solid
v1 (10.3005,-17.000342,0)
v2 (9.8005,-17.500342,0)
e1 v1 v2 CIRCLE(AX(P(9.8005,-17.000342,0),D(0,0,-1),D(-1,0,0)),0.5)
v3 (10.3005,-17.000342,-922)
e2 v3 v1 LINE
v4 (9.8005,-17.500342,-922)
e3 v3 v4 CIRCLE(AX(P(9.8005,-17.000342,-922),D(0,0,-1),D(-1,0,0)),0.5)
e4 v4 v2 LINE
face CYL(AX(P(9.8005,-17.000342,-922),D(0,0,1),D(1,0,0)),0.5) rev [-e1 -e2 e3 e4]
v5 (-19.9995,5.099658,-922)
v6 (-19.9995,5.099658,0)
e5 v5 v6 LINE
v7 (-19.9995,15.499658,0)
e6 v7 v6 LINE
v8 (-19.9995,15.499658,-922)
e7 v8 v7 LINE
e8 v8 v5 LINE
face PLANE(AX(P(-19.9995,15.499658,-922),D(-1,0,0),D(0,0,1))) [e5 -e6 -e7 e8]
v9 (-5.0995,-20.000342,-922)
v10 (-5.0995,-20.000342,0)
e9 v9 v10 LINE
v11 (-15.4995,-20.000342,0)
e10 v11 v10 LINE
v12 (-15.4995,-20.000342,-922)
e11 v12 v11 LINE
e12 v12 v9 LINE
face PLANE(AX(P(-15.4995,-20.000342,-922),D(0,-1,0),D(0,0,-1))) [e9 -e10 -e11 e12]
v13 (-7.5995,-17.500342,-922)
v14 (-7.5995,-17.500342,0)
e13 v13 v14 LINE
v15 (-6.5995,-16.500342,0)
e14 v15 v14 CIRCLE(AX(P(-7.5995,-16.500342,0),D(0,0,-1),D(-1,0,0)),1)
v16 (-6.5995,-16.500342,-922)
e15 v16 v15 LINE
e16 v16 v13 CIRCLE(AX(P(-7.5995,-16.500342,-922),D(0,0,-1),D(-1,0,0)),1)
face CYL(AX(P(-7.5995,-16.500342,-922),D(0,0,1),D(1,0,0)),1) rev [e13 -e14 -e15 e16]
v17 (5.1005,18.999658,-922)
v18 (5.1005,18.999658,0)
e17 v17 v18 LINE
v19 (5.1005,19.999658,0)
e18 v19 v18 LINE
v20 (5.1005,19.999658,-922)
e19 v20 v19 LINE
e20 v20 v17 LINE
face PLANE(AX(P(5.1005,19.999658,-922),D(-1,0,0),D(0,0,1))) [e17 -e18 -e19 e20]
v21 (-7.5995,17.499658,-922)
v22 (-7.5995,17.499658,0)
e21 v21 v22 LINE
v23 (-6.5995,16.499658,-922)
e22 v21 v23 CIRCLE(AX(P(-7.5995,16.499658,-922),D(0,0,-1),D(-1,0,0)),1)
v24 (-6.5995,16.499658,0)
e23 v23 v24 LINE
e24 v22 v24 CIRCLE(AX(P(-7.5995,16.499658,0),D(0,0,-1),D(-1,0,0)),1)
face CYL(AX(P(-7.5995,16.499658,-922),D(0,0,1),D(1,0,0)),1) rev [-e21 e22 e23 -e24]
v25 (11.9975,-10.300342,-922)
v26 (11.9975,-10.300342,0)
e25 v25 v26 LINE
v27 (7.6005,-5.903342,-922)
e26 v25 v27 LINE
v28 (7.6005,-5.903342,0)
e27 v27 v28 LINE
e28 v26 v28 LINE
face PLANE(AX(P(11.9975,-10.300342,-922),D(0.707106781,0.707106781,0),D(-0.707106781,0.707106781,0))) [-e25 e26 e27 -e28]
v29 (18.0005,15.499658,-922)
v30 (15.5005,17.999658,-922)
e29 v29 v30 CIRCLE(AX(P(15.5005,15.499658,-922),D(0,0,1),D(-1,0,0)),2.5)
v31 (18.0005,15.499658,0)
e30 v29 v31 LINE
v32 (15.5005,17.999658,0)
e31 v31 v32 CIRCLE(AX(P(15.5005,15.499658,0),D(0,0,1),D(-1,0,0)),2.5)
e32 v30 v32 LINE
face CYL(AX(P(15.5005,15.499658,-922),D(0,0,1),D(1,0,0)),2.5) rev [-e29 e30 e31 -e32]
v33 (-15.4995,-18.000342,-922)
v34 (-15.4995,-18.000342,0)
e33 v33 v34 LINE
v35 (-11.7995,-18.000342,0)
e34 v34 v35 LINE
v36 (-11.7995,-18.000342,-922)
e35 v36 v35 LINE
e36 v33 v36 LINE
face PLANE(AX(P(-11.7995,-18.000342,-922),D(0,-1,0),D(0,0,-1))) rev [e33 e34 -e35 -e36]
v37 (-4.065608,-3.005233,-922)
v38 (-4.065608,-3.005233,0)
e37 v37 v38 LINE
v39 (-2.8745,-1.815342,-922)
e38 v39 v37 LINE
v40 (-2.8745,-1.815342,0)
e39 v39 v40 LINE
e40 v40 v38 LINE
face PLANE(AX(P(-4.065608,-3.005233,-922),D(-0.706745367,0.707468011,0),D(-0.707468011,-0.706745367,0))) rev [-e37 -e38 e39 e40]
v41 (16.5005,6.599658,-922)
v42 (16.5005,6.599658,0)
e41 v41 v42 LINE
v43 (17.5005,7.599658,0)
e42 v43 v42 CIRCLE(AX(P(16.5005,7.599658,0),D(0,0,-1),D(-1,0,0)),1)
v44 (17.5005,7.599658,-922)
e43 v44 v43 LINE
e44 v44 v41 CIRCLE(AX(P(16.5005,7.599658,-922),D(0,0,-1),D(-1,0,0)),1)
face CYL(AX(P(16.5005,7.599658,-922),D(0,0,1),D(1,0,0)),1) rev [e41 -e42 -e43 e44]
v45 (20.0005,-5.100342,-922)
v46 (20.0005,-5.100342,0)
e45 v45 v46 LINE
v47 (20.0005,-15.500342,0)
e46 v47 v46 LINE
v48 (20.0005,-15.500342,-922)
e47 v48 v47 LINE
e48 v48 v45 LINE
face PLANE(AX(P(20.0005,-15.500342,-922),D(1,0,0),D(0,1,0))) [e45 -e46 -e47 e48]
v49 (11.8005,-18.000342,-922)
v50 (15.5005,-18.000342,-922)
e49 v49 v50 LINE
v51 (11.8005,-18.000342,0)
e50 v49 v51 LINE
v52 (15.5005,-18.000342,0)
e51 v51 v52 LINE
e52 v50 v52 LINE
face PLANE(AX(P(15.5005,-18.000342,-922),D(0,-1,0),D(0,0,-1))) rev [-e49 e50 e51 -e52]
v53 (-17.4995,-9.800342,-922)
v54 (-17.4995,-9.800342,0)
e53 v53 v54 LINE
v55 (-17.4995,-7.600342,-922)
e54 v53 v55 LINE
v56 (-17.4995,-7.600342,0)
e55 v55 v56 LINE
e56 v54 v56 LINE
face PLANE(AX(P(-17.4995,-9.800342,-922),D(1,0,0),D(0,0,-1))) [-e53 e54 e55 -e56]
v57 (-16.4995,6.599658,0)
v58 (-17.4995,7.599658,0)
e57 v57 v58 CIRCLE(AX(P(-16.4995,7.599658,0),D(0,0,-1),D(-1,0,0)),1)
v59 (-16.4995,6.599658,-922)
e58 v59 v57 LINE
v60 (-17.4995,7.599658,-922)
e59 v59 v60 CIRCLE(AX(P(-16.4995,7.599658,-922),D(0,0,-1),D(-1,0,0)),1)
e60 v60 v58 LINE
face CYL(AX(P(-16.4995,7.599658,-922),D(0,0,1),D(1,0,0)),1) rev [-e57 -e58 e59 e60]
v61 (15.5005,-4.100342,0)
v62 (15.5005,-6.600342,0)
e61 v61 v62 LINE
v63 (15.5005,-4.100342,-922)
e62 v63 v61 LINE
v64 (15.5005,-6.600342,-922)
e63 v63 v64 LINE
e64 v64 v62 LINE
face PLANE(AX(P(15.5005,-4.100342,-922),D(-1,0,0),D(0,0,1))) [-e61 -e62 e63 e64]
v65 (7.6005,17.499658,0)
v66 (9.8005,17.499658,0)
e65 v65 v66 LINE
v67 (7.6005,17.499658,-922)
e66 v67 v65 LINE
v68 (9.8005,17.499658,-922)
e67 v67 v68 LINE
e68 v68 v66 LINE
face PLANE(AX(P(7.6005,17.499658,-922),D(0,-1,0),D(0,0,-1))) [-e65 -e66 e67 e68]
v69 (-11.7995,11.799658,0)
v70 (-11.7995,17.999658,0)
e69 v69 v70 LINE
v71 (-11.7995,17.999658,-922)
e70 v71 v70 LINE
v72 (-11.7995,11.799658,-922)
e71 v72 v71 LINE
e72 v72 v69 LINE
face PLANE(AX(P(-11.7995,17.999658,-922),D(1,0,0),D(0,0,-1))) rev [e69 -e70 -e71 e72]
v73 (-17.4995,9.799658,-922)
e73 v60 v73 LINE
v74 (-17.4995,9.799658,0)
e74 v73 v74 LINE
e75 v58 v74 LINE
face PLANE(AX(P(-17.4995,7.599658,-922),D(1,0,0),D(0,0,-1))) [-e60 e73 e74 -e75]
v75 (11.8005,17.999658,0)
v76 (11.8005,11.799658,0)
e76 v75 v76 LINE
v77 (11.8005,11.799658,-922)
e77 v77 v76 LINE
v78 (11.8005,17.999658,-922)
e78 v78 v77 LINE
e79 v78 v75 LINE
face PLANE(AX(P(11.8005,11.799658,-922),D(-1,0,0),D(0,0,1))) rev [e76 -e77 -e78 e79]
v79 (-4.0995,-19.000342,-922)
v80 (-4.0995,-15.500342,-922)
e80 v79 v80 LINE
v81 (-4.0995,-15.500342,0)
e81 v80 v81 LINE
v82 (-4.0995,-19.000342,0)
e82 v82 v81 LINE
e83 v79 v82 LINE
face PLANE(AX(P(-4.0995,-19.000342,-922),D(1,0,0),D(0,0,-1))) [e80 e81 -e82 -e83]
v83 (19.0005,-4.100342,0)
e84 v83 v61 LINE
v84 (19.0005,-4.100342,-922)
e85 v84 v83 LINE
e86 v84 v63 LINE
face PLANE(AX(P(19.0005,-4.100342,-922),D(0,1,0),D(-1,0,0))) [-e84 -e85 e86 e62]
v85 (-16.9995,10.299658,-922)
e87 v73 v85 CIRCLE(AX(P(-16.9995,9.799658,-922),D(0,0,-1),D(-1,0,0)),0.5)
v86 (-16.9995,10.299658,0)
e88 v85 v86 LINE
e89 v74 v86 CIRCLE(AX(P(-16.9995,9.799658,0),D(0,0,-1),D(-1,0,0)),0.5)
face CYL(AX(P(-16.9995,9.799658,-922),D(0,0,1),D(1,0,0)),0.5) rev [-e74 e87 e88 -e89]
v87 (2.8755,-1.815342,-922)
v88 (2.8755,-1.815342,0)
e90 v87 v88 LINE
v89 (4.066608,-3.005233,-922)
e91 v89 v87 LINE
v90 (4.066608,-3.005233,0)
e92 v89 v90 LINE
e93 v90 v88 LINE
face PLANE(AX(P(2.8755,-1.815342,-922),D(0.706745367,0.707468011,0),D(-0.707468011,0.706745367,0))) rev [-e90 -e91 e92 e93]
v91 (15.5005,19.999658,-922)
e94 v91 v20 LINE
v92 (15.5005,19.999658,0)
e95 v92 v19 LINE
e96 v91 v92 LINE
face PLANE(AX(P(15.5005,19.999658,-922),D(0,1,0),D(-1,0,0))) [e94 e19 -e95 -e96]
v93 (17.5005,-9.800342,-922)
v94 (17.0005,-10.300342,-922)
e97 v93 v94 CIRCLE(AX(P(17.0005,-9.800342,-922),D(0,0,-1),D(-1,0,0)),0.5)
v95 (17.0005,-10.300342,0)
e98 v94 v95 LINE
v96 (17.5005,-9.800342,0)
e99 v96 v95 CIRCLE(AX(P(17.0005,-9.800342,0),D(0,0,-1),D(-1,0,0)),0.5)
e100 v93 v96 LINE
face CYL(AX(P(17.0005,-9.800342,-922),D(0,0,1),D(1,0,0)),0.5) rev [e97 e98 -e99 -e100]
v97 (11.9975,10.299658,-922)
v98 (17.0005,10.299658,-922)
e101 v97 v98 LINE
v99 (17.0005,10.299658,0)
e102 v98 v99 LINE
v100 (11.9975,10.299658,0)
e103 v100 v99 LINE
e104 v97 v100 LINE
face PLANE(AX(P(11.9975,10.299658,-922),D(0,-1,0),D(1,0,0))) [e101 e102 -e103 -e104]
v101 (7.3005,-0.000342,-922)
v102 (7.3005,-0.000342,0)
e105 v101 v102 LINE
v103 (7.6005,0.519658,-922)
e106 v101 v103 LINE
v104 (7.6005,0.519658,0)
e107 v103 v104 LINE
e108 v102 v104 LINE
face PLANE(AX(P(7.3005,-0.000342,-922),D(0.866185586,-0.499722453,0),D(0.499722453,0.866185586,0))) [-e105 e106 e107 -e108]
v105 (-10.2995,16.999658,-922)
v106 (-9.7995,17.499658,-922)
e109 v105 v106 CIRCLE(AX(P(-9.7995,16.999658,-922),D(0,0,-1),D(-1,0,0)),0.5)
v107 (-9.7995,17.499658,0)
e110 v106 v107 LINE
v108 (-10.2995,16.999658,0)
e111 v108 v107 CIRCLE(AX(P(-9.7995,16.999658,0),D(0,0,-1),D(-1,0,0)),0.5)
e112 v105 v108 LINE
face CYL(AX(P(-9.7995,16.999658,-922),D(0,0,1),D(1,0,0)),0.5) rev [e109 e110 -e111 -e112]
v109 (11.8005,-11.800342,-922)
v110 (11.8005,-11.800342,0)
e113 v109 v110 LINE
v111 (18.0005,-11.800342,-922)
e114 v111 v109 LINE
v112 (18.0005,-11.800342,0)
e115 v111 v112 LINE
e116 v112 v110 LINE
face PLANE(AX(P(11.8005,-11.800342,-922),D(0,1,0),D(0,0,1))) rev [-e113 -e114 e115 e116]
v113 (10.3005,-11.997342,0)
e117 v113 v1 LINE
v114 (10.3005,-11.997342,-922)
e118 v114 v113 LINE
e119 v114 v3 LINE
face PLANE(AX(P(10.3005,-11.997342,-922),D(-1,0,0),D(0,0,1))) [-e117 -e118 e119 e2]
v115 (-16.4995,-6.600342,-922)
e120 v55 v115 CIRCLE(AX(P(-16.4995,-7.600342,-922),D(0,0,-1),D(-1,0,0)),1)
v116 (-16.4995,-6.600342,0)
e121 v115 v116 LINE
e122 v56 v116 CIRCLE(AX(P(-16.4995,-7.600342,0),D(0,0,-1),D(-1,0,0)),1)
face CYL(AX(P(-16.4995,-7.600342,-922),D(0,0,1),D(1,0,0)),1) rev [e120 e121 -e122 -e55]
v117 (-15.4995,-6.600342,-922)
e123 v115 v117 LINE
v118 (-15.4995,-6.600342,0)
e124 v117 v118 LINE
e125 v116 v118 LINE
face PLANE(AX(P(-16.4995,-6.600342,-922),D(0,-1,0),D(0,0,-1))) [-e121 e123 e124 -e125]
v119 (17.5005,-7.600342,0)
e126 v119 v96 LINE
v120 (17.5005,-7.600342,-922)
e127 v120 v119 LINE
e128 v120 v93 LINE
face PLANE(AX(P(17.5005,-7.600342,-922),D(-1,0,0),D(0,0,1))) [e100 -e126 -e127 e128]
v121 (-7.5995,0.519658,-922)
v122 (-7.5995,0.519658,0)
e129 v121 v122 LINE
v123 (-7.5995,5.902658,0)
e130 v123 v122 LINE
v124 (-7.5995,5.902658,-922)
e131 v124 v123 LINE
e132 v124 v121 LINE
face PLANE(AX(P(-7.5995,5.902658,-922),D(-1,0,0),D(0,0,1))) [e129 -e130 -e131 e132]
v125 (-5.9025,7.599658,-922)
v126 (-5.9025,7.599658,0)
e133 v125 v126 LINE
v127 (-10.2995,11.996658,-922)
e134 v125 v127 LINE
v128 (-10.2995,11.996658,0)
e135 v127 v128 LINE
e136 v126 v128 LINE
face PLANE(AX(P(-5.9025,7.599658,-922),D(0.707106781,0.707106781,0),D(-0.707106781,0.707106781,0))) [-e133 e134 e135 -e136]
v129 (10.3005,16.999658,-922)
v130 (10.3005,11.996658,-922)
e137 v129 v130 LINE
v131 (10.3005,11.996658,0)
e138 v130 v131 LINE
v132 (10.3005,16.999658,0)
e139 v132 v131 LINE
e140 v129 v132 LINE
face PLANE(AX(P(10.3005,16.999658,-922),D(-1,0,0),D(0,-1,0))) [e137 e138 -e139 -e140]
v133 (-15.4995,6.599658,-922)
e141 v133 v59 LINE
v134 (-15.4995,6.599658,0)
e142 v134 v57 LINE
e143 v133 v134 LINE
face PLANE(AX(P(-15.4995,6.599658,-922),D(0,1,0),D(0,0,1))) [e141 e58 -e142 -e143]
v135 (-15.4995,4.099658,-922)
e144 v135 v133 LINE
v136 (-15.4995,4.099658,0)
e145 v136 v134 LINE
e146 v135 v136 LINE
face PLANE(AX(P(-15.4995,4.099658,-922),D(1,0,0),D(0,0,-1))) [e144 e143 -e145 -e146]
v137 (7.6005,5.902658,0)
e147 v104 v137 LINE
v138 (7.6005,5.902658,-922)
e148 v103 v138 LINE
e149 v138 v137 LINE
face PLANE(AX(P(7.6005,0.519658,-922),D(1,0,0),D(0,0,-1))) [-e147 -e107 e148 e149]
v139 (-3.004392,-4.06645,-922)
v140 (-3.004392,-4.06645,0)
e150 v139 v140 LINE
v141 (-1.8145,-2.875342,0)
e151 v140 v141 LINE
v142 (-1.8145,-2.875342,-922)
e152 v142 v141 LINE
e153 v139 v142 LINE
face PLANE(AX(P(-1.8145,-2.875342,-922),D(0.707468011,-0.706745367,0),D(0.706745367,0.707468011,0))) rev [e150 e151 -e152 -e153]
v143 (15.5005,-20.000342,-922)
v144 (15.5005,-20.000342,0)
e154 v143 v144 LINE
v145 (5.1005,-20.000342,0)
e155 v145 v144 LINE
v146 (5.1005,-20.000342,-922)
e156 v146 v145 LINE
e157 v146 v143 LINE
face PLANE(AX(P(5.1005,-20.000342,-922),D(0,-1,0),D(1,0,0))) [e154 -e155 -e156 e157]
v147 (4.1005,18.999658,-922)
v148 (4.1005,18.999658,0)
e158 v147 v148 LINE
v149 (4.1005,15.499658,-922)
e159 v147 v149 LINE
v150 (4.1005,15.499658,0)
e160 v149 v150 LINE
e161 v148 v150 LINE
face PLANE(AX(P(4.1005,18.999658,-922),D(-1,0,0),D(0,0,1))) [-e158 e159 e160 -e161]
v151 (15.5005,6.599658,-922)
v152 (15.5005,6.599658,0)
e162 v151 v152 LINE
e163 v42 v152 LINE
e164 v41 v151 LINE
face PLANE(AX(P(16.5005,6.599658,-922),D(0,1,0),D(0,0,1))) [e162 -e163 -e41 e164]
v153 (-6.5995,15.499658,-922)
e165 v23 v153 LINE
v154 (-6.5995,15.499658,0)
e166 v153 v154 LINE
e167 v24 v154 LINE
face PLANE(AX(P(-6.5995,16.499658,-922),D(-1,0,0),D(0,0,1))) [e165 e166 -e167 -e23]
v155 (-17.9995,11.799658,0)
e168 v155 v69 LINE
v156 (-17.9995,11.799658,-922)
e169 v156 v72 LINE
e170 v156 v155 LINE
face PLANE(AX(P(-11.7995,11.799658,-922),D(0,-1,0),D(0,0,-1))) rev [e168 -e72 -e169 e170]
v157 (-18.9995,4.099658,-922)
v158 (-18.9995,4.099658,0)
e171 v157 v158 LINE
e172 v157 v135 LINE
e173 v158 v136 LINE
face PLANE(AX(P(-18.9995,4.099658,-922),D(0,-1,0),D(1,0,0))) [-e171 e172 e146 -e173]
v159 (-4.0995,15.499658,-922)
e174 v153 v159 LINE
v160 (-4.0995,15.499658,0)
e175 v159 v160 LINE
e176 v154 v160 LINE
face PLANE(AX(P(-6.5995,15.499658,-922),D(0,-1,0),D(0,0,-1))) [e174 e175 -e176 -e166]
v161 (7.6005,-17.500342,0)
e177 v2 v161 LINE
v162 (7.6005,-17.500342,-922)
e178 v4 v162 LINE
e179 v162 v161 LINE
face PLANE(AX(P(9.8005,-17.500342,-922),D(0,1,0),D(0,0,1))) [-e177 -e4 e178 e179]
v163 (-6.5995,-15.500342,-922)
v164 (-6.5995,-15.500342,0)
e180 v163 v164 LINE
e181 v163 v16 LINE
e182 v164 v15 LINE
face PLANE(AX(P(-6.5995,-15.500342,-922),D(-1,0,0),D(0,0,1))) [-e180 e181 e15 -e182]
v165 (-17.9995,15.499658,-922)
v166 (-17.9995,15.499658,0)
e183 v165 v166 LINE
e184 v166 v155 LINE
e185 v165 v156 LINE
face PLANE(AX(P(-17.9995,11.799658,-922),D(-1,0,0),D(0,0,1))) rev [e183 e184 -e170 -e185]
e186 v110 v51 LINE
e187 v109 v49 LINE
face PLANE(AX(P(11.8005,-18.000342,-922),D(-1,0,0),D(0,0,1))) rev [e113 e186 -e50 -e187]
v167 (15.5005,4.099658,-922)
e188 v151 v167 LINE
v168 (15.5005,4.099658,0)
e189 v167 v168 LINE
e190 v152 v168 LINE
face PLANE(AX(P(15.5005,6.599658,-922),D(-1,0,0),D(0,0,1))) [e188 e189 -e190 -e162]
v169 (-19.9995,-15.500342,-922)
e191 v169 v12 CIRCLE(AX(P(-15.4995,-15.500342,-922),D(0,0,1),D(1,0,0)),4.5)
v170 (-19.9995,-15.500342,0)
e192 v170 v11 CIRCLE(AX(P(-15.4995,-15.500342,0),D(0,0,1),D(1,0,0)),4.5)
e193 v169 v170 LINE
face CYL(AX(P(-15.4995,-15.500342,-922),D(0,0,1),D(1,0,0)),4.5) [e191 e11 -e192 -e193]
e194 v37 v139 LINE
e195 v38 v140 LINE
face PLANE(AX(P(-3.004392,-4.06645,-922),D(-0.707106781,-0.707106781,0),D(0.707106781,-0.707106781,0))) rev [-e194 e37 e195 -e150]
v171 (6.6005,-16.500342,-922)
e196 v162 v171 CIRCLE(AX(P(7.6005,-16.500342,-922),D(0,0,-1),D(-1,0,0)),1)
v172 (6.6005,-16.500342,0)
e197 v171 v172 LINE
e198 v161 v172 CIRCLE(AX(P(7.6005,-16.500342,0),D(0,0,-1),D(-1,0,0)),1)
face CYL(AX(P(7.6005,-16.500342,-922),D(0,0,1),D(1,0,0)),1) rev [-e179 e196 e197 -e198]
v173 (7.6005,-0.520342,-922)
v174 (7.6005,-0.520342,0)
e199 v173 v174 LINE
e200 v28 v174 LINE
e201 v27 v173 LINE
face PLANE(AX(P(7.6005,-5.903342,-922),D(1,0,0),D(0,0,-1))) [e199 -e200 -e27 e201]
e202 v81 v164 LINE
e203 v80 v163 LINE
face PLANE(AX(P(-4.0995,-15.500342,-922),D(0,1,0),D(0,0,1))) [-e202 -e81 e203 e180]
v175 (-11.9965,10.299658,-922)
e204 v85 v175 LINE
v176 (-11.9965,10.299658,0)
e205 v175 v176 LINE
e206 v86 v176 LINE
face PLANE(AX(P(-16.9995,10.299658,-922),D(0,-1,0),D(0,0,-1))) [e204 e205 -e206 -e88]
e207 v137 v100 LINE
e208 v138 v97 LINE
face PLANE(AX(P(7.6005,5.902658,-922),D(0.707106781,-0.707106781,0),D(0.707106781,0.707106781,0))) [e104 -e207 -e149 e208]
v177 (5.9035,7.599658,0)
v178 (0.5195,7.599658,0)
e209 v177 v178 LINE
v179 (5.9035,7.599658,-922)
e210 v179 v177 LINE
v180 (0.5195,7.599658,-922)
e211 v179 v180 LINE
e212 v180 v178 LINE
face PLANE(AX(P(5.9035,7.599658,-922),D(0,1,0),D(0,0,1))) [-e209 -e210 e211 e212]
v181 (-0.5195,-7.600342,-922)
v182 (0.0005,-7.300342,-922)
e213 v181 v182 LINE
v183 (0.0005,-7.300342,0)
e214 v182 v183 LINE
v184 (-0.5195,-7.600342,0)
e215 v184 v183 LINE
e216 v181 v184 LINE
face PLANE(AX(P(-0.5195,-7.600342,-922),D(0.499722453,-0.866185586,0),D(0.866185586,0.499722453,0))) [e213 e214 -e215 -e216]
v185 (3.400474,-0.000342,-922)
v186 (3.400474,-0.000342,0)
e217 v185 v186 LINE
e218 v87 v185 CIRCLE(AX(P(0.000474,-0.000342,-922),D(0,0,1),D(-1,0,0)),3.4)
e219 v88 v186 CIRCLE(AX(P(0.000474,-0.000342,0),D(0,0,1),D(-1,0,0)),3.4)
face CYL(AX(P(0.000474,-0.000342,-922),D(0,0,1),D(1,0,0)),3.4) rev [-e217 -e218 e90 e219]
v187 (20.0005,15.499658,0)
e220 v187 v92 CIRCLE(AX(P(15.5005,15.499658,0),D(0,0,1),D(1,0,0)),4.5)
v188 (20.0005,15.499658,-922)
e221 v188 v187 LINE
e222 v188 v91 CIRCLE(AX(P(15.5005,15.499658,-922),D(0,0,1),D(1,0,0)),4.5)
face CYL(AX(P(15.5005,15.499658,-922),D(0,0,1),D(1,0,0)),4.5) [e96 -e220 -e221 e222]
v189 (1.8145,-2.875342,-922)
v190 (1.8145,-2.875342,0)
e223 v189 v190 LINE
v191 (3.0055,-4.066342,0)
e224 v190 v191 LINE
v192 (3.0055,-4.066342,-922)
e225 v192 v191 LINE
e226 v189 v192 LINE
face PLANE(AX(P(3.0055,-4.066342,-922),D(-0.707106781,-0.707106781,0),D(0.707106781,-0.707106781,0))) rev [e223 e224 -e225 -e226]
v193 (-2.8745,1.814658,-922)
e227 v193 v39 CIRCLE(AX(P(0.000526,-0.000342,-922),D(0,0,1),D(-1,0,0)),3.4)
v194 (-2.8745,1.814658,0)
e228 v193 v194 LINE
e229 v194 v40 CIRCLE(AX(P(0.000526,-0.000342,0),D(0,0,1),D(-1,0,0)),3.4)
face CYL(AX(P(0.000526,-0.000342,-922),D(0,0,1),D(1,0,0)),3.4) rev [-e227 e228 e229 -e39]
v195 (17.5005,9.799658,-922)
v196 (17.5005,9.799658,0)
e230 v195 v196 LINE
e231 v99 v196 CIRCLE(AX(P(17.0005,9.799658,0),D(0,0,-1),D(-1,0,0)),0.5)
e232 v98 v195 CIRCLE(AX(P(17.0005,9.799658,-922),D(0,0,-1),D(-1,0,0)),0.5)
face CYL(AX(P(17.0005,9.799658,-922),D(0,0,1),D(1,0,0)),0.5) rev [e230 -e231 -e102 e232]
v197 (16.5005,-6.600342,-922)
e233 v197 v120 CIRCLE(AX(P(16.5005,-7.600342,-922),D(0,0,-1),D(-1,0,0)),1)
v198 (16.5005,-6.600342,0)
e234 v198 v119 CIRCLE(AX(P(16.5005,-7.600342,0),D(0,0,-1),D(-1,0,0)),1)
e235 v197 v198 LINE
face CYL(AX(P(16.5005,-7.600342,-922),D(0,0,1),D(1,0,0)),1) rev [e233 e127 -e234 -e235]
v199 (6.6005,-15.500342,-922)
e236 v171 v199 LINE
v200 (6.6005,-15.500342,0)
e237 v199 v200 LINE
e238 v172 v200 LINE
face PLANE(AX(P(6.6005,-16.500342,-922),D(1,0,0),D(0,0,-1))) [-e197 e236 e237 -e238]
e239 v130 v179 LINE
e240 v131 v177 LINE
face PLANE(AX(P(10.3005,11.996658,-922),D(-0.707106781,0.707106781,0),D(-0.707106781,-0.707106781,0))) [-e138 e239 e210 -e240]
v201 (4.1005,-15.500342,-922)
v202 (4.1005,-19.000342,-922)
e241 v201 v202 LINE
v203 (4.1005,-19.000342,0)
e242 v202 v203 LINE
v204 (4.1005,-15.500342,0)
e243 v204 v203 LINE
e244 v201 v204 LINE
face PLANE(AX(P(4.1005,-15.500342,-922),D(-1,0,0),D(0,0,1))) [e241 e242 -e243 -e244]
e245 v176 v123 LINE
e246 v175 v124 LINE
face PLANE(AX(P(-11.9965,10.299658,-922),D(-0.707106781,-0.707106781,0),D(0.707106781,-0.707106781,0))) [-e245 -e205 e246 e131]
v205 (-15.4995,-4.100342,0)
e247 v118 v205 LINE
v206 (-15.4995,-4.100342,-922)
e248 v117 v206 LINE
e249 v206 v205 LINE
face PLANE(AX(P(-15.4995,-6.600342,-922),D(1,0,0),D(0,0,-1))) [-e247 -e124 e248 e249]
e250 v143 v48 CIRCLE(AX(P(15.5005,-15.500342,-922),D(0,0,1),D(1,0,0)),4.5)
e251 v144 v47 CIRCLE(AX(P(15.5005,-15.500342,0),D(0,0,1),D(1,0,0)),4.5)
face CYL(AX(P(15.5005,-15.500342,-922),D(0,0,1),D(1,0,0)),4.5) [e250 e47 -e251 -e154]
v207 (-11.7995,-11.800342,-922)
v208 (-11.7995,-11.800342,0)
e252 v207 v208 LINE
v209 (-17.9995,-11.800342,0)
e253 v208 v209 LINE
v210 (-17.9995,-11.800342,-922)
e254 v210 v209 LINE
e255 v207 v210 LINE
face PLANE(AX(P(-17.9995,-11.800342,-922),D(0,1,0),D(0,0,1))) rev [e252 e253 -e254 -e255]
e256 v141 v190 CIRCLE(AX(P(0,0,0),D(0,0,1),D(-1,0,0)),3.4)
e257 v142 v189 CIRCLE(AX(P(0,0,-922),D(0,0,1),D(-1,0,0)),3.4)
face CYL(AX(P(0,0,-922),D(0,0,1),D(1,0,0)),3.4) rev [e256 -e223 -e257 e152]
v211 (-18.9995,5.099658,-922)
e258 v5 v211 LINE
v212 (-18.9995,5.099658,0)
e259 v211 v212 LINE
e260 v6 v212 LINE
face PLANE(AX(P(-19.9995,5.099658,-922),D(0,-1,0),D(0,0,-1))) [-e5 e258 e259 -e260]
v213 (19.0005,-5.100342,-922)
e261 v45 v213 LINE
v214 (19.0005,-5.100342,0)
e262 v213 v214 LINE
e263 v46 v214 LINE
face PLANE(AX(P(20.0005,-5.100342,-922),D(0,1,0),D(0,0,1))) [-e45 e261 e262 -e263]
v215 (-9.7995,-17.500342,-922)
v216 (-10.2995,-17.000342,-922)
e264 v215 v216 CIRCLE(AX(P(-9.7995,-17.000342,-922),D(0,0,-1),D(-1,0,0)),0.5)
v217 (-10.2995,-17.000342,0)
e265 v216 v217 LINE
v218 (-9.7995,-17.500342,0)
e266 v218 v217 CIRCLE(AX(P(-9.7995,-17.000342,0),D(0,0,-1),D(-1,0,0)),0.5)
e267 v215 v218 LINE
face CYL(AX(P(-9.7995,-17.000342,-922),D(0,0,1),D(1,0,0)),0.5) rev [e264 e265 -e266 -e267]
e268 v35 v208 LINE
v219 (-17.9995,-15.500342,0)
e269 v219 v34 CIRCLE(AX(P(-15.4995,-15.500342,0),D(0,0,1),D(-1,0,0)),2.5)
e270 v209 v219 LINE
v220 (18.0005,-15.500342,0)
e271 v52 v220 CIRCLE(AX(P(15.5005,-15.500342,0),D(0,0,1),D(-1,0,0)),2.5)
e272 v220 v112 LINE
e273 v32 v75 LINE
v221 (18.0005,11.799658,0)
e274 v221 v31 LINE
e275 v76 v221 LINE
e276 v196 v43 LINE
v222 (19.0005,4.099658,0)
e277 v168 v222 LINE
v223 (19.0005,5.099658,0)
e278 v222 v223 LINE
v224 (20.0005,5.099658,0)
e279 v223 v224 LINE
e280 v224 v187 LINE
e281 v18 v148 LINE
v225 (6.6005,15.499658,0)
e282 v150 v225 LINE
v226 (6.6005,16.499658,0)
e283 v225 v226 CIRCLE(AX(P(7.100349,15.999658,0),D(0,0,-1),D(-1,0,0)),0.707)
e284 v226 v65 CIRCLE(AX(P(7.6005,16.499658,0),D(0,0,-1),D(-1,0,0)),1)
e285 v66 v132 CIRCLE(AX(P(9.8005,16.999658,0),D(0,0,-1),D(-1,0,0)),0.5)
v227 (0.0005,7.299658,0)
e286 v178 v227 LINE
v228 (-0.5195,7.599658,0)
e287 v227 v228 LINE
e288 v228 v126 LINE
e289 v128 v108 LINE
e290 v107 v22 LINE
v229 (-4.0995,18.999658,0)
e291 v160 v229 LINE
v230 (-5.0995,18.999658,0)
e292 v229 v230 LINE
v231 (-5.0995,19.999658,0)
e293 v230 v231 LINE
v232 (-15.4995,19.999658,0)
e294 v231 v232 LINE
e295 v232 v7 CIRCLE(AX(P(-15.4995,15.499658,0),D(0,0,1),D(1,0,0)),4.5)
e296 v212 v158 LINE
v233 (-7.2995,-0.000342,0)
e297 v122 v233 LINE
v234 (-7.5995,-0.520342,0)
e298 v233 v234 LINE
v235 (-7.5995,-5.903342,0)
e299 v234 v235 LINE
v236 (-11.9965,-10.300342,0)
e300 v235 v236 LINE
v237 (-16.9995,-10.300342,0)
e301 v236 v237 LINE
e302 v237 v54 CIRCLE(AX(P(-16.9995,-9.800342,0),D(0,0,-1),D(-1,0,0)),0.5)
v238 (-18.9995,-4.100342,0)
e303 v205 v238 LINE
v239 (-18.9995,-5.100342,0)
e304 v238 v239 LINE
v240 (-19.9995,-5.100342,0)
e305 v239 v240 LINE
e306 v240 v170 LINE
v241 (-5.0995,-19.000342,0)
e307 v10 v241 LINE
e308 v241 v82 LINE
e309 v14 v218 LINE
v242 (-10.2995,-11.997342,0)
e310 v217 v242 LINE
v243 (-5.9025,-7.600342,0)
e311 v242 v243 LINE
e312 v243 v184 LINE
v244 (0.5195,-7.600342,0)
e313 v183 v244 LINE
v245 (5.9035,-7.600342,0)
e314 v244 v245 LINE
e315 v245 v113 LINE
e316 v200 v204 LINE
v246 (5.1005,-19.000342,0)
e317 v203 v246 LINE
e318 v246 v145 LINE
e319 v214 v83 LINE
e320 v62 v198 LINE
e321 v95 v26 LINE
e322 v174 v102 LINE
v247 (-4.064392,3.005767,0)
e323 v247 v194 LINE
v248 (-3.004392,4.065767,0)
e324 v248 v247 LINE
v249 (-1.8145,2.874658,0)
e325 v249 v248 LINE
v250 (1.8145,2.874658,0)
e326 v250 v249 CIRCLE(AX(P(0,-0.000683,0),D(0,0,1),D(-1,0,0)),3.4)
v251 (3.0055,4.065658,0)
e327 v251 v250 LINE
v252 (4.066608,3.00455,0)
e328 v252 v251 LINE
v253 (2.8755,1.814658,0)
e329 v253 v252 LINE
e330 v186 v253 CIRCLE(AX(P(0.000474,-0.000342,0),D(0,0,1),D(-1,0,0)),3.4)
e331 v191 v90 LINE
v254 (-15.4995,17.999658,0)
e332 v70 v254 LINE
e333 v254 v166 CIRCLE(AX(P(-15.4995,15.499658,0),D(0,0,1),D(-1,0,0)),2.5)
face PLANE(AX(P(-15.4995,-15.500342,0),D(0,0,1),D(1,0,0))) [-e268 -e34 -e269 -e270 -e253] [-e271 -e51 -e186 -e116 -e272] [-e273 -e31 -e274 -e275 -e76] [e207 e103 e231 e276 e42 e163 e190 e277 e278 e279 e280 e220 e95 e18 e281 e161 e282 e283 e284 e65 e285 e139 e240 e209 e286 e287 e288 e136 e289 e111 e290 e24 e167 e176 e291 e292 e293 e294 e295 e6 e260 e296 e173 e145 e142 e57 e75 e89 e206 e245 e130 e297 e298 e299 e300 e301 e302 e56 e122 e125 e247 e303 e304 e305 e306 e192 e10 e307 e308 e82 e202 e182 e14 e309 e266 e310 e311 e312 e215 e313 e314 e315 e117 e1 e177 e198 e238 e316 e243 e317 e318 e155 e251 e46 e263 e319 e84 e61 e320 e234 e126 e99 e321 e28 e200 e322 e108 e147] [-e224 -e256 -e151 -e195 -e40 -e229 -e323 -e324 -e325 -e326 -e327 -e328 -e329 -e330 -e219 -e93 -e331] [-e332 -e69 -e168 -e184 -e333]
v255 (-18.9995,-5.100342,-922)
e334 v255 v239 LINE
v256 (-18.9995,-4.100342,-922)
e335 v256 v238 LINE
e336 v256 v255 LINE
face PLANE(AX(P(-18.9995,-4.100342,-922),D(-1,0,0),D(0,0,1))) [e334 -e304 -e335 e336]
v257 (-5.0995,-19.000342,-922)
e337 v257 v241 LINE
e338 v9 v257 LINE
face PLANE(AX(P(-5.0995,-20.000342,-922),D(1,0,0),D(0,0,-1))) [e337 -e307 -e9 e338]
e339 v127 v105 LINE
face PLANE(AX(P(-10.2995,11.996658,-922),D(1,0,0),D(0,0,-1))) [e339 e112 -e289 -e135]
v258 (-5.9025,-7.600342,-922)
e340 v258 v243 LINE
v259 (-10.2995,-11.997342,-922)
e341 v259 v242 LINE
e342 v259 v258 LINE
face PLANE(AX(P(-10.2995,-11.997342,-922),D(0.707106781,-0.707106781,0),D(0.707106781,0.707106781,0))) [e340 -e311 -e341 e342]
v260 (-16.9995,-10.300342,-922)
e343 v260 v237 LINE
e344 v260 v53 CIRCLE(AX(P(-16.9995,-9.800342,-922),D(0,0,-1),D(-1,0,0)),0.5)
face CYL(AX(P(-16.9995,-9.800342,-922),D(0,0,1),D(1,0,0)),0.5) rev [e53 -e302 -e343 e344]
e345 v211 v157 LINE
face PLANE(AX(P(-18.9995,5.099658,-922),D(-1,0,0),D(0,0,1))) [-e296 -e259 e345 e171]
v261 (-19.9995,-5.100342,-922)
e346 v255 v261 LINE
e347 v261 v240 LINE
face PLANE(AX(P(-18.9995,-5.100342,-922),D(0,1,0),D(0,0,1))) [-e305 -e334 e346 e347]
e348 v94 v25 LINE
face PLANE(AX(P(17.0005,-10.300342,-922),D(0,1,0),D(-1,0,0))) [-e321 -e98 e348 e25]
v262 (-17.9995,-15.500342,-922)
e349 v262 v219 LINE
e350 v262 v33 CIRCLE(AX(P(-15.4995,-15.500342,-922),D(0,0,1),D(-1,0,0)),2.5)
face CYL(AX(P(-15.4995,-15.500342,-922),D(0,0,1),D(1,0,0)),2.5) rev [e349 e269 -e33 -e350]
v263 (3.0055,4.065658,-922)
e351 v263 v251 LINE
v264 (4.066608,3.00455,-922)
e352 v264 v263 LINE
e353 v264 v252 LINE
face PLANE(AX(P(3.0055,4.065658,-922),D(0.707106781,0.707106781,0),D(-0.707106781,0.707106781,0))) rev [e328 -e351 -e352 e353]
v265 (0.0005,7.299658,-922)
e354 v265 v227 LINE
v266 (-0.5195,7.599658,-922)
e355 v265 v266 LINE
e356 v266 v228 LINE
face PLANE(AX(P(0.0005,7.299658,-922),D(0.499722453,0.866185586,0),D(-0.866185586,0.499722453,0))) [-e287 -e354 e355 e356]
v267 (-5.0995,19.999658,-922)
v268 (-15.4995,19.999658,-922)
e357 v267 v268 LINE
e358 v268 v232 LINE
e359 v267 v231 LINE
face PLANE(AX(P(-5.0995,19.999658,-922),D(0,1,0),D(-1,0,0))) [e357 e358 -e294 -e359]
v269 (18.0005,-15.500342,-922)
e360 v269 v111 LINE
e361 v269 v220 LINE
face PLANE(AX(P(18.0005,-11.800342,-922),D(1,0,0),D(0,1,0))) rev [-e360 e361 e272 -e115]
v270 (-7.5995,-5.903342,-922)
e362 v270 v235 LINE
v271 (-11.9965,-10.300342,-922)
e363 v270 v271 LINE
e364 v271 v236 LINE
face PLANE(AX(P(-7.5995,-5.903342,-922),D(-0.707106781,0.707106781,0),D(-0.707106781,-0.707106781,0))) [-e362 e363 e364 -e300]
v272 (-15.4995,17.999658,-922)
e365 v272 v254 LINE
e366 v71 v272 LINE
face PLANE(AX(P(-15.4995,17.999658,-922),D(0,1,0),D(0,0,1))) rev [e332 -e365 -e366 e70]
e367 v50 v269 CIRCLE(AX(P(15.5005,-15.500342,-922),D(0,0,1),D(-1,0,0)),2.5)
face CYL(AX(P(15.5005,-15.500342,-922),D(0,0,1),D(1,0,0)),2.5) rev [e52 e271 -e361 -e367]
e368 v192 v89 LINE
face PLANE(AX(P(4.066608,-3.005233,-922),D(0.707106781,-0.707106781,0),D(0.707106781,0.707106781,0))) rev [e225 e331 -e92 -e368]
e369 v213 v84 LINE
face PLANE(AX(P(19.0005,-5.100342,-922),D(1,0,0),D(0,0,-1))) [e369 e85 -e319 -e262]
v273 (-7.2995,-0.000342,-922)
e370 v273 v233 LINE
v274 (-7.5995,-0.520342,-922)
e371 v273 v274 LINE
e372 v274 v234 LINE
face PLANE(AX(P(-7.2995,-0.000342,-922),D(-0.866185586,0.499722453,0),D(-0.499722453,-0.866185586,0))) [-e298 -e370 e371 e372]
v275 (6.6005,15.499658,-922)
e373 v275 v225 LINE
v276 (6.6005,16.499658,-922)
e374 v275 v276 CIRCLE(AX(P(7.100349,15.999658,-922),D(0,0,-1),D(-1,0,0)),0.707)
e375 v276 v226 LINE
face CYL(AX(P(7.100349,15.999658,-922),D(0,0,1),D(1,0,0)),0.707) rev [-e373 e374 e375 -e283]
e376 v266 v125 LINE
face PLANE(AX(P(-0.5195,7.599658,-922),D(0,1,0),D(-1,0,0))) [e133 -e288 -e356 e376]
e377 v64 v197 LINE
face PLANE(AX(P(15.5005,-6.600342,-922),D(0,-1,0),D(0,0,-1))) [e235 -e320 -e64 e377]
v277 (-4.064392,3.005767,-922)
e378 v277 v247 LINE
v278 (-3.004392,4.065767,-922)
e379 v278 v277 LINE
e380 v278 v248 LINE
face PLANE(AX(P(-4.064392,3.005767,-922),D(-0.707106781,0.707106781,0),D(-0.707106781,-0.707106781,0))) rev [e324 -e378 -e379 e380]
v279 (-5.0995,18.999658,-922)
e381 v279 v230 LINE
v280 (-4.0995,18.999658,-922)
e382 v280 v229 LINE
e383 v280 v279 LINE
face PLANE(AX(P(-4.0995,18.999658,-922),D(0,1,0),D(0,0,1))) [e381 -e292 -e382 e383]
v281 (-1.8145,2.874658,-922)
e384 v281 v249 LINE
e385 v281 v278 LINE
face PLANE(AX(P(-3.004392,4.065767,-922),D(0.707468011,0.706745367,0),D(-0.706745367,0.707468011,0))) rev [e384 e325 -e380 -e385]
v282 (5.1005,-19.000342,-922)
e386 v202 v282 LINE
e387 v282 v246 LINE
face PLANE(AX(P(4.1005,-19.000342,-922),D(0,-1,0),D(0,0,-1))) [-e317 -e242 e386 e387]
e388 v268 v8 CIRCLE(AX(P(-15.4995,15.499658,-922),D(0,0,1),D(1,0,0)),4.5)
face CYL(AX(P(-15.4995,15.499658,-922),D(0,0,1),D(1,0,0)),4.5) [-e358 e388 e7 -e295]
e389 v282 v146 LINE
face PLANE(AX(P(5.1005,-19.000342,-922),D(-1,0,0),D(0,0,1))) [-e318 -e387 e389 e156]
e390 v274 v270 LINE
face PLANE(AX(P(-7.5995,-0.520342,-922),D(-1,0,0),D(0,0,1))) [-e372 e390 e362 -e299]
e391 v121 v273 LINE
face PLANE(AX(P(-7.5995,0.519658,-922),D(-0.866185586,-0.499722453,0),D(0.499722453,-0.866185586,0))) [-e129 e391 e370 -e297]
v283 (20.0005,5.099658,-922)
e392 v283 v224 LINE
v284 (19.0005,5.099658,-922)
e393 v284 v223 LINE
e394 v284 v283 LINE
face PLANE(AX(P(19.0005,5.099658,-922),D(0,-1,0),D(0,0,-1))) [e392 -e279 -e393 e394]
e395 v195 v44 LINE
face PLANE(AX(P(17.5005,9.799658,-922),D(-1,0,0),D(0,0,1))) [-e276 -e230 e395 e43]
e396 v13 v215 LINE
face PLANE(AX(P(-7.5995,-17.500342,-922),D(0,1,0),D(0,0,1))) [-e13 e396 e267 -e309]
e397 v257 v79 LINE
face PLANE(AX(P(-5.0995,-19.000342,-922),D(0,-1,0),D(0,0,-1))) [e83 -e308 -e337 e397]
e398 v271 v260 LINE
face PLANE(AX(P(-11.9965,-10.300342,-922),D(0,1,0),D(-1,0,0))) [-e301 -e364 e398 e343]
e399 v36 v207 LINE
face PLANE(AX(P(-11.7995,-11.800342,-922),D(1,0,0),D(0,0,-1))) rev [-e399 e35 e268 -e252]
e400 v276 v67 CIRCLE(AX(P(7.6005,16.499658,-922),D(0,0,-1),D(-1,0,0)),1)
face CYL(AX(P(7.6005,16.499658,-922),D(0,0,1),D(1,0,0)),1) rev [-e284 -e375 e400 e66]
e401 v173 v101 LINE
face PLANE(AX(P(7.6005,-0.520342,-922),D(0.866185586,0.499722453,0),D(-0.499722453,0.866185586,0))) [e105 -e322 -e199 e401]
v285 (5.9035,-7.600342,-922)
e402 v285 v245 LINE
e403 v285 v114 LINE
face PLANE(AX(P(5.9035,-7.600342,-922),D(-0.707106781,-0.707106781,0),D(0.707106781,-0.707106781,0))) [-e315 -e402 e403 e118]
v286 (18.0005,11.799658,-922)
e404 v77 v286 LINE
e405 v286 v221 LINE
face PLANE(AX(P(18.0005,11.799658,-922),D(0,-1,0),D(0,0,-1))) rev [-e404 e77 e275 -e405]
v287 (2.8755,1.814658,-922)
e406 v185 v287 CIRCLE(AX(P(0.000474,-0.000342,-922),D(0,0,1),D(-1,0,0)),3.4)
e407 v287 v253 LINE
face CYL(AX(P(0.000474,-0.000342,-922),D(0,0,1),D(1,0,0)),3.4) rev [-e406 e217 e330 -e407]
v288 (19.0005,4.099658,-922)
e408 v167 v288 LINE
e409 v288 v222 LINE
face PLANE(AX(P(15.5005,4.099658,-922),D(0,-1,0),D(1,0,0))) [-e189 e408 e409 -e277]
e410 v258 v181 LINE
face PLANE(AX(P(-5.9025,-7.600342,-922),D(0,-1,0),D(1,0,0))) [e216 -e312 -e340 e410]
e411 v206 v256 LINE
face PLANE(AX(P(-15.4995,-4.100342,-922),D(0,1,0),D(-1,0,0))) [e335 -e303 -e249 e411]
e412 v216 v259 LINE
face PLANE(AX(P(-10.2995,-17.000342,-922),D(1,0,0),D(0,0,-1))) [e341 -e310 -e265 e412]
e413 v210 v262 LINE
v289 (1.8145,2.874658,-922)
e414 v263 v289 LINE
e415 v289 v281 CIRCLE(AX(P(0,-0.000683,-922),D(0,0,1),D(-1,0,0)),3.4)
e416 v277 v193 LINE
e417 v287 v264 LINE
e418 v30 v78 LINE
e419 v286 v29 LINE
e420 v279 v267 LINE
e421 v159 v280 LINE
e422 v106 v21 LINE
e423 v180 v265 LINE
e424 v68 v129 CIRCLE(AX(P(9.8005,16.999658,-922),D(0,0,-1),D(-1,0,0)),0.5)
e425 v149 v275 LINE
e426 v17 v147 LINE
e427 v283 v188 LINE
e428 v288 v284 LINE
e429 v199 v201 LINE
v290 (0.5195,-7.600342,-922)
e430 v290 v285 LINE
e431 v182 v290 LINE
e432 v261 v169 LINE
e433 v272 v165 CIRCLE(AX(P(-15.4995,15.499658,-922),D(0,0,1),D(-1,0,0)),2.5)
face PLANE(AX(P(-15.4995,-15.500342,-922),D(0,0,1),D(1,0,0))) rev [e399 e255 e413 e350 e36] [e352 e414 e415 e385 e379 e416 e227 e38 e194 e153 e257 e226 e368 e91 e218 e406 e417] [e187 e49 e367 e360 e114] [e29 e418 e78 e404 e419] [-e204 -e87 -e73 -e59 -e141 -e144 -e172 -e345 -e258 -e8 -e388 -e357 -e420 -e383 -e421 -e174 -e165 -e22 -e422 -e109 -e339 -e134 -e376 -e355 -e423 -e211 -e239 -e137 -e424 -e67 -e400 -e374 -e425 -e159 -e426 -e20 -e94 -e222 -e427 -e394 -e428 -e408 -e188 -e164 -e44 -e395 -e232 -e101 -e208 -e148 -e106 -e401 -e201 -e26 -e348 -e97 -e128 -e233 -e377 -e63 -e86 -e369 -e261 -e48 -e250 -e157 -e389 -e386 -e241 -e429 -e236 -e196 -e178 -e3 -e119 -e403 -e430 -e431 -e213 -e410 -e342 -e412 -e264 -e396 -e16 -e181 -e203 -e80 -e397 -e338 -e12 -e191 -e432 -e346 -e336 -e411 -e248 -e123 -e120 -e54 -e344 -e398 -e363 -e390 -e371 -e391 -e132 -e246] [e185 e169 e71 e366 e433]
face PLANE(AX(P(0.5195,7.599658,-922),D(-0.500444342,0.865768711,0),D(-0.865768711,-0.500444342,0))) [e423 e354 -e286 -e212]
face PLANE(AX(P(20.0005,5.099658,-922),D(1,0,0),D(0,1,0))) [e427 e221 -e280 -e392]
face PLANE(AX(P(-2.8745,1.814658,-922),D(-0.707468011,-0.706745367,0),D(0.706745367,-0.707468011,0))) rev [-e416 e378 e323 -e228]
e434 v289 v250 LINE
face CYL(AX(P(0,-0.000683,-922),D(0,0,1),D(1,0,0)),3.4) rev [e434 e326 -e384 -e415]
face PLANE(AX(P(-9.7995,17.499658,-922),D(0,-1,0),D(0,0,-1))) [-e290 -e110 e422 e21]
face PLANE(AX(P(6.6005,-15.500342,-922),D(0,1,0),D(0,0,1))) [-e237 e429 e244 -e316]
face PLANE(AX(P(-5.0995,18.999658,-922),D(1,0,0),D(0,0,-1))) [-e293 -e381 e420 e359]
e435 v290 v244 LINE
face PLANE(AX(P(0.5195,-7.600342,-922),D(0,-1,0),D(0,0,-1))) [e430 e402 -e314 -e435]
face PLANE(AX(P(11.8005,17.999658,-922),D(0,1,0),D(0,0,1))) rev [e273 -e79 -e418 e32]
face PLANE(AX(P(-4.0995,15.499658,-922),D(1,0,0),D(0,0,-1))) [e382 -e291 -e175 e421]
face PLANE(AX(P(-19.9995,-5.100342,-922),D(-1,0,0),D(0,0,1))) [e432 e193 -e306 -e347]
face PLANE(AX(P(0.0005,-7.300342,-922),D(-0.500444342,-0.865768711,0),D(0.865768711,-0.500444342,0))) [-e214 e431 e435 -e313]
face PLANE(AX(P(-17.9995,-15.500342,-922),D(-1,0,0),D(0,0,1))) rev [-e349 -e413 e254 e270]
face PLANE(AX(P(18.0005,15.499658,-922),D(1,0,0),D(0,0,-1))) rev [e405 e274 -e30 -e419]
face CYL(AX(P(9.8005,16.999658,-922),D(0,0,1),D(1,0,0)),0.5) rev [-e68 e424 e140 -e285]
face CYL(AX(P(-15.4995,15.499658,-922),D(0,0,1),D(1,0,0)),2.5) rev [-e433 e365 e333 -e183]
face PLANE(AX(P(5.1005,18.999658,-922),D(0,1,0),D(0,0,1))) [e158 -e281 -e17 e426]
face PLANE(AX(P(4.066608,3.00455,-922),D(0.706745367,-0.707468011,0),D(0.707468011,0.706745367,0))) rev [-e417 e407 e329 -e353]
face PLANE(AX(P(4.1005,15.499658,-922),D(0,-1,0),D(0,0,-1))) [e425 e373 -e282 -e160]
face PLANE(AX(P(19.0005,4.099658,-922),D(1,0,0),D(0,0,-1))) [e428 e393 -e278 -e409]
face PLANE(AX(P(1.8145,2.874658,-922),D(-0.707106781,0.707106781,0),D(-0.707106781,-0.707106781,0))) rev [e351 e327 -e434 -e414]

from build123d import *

# Parameters (mm, degrees)
EXTRUDE_1_DEPTH = 922


with BuildPart() as part:
    # 草图1 → 凸台-拉伸1 (new body)
    with BuildSketch(Plane.XY):
        with BuildLine():
            Line((-18.9995, -4.100341675), (-18.9995, -5.100341675))
            Line((-18.9995, -5.100341675), (-19.9995, -5.100341675))
            Line((-19.9995, -5.100341675), (-19.9995, -15.500341675))
            ThreePointArc((-19.9995, -15.500341675), (-18.681480515, -18.682322191), (-15.4995, -20.000341675))
            Line((-15.4995, -20.000341675), (-5.0995, -20.000341675))
            Line((-5.0995, -20.000341675), (-5.0995, -19.000341675))
            Line((-5.0995, -19.000341675), (-4.0995, -19.000341675))
            Line((-4.0995, -19.000341675), (-4.0995, -15.500341675))
            Line((-4.0995, -15.500341675), (-6.5995, -15.500341675))
            Line((-6.5995, -15.500341675), (-6.5995, -16.500341675))
            ThreePointArc((-6.5995, -16.500341675), (-6.892393219, -17.207448457), (-7.5995, -17.500341675))
            Line((-7.5995, -17.500341675), (-9.7995, -17.500341675))
            ThreePointArc((-9.7995, -17.500341675), (-10.153053391, -17.353895066), (-10.2995, -17.000341675))
            Line((-10.2995, -17.000341675), (-10.2995, -11.997341675))
            Line((-10.2995, -11.997341675), (-5.9025, -7.600341675))
            Line((-5.9025, -7.600341675), (-0.5195, -7.600341675))
            Line((-0.5195, -7.600341675), (0.0005, -7.300341675))
            Line((0.0005, -7.300341675), (0.5195, -7.600341675))
            Line((0.5195, -7.600341675), (5.9035, -7.600341675))
            Line((5.9035, -7.600341675), (10.3005, -11.997341675))
            Line((10.3005, -11.997341675), (10.3005, -17.000341675))
            ThreePointArc((10.3005, -17.000341675), (10.154053391, -17.353895066), (9.8005, -17.500341675))
            Line((9.8005, -17.500341675), (7.6005, -17.500341675))
            ThreePointArc((7.6005, -17.500341675), (6.893393219, -17.207448457), (6.6005, -16.500341675))
            Line((6.6005, -16.500341675), (6.6005, -15.500341675))
            Line((6.6005, -15.500341675), (4.1005, -15.500341675))
            Line((4.1005, -15.500341675), (4.1005, -19.000341675))
            Line((4.1005, -19.000341675), (5.1005, -19.000341675))
            Line((5.1005, -19.000341675), (5.1005, -20.000341675))
            Line((5.1005, -20.000341675), (15.5005, -20.000341675))
            ThreePointArc((15.5005, -20.000341675), (18.682480515, -18.682322191), (20.0005, -15.500341675))
            Line((20.0005, -15.500341675), (20.0005, -5.100341675))
            Line((20.0005, -5.100341675), (19.0005, -5.100341675))
            Line((19.0005, -5.100341675), (19.0005, -4.100341675))
            Line((19.0005, -4.100341675), (15.5005, -4.100341675))
            Line((15.5005, -4.100341675), (15.5005, -6.600341675))
            Line((15.5005, -6.600341675), (16.5005, -6.600341675))
            ThreePointArc((16.5005, -6.600341675), (17.207606781, -6.893234894), (17.5005, -7.600341675))
            Line((17.5005, -7.600341675), (17.5005, -9.800341675))
            ThreePointArc((17.5005, -9.800341675), (17.354053391, -10.153895066), (17.0005, -10.300341675))
            Line((17.0005, -10.300341675), (11.9975, -10.300341675))
            Line((11.9975, -10.300341675), (7.6005, -5.903341675))
            Line((7.6005, -5.903341675), (7.6005, -0.520341675))
            Line((7.6005, -0.520341675), (7.3005, -0.000341675))
            Line((7.3005, -0.000341675), (7.6005, 0.519658325))
            Line((7.6005, 0.519658325), (7.6005, 5.902658325))
            Line((7.6005, 5.902658325), (11.9975, 10.299658325))
            Line((11.9975, 10.299658325), (17.0005, 10.299658325))
            ThreePointArc((17.0005, 10.299658325), (17.354053391, 10.153211715), (17.5005, 9.799658325))
            Line((17.5005, 9.799658325), (17.5005, 7.599658325))
            ThreePointArc((17.5005, 7.599658325), (17.207606781, 6.892551543), (16.5005, 6.599658325))
            Line((16.5005, 6.599658325), (15.5005, 6.599658325))
            Line((15.5005, 6.599658325), (15.5005, 4.099658325))
            Line((15.5005, 4.099658325), (19.0005, 4.099658325))
            Line((19.0005, 4.099658325), (19.0005, 5.099658325))
            Line((19.0005, 5.099658325), (20.0005, 5.099658325))
            Line((20.0005, 5.099658325), (20.0005, 15.499658325))
            ThreePointArc((20.0005, 15.499658325), (18.682480515, 18.68163884), (15.5005, 19.999658325))
            Line((15.5005, 19.999658325), (5.1005, 19.999658325))
            Line((5.1005, 19.999658325), (5.1005, 18.999658325))
            Line((5.1005, 18.999658325), (4.1005, 18.999658325))
            Line((4.1005, 18.999658325), (4.1005, 15.499658325))
            Line((4.1005, 15.499658325), (6.6005, 15.499658325))
            ThreePointArc((6.6005, 15.499658325), (6.393348977, 15.999658325), (6.6005, 16.499658325))
            ThreePointArc((6.6005, 16.499658325), (6.893393219, 17.206765106), (7.6005, 17.499658325))
            Line((7.6005, 17.499658325), (9.8005, 17.499658325))
            ThreePointArc((9.8005, 17.499658325), (10.154053391, 17.353211715), (10.3005, 16.999658325))
            Line((10.3005, 16.999658325), (10.3005, 11.996658325))
            Line((10.3005, 11.996658325), (5.9035, 7.599658325))
            Line((5.9035, 7.599658325), (0.5195, 7.599658325))
            Line((0.5195, 7.599658325), (0.0005, 7.299658325))
            Line((0.0005, 7.299658325), (-0.5195, 7.599658325))
            Line((-0.5195, 7.599658325), (-5.9025, 7.599658325))
            Line((-5.9025, 7.599658325), (-10.2995, 11.996658325))
            Line((-10.2995, 11.996658325), (-10.2995, 16.999658325))
            ThreePointArc((-10.2995, 16.999658325), (-10.153053391, 17.353211715), (-9.7995, 17.499658325))
            Line((-9.7995, 17.499658325), (-7.5995, 17.499658325))
            ThreePointArc((-7.5995, 17.499658325), (-6.892393219, 17.206765106), (-6.5995, 16.499658325))
            Line((-6.5995, 16.499658325), (-6.5995, 15.499658325))
            Line((-6.5995, 15.499658325), (-4.0995, 15.499658325))
            Line((-4.0995, 15.499658325), (-4.0995, 18.999658325))
            Line((-4.0995, 18.999658325), (-5.0995, 18.999658325))
            Line((-5.0995, 18.999658325), (-5.0995, 19.999658325))
            Line((-5.0995, 19.999658325), (-15.4995, 19.999658325))
            ThreePointArc((-15.4995, 19.999658325), (-18.681480515, 18.68163884), (-19.9995, 15.499658325))
            Line((-19.9995, 15.499658325), (-19.9995, 5.099658325))
            Line((-19.9995, 5.099658325), (-18.9995, 5.099658325))
            Line((-18.9995, 5.099658325), (-18.9995, 4.099658325))
            Line((-18.9995, 4.099658325), (-15.4995, 4.099658325))
            Line((-15.4995, 4.099658325), (-15.4995, 6.599658325))
            Line((-15.4995, 6.599658325), (-16.4995, 6.599658325))
            ThreePointArc((-16.4995, 6.599658325), (-17.206606781, 6.892551543), (-17.4995, 7.599658325))
            Line((-17.4995, 7.599658325), (-17.4995, 9.799658325))
            ThreePointArc((-17.4995, 9.799658325), (-17.353053391, 10.153211715), (-16.9995, 10.299658325))
            Line((-16.9995, 10.299658325), (-11.9965, 10.299658325))
            Line((-11.9965, 10.299658325), (-7.5995, 5.902658325))
            Line((-7.5995, 5.902658325), (-7.5995, 0.519658325))
            Line((-7.5995, 0.519658325), (-7.2995, -0.000341675))
            Line((-7.2995, -0.000341675), (-7.5995, -0.520341675))
            Line((-7.5995, -0.520341675), (-7.5995, -5.903341675))
            Line((-7.5995, -5.903341675), (-11.9965, -10.300341675))
            Line((-11.9965, -10.300341675), (-16.9995, -10.300341675))
            ThreePointArc((-16.9995, -10.300341675), (-17.353053391, -10.153895066), (-17.4995, -9.800341675))
            Line((-17.4995, -9.800341675), (-17.4995, -7.600341675))
            ThreePointArc((-17.4995, -7.600341675), (-17.206606781, -6.893234894), (-16.4995, -6.600341675))
            Line((-16.4995, -6.600341675), (-15.4995, -6.600341675))
            Line((-15.4995, -6.600341675), (-15.4995, -4.100341675))
            Line((-15.4995, -4.100341675), (-18.9995, -4.100341675))
        make_face()
        with BuildLine():
            Line((15.5005, -18.000341675), (11.8005, -18.000341675))
            Line((11.8005, -18.000341675), (11.8005, -11.800341675))
            Line((11.8005, -11.800341675), (18.0005, -11.800341675))
            Line((18.0005, -11.800341675), (18.0005, -15.500341675))
            ThreePointArc((18.0005, -15.500341675), (17.268266953, -17.268108628), (15.5005, -18.000341675))
        make_face(mode=Mode.SUBTRACT)
        with BuildLine():
            Line((18.0005, 11.799658325), (11.8005, 11.799658325))
            Line((11.8005, 11.799658325), (11.8005, 17.999658325))
            Line((11.8005, 17.999658325), (15.5005, 17.999658325))
            ThreePointArc((15.5005, 17.999658325), (17.268266953, 17.267425278), (18.0005, 15.499658325))
            Line((18.0005, 15.499658325), (18.0005, 11.799658325))
        make_face(mode=Mode.SUBTRACT)
        with BuildLine():
            Line((-1.8145, -2.875341675), (-3.004391671, -4.066450004))
            Line((-3.004391671, -4.066450004), (-4.065608329, -3.005233346))
            Line((-4.065608329, -3.005233346), (-2.8745, -1.815341675))
            ThreePointArc((-2.8745, -1.815341675), (-3.399473913, -0.000341675), (-2.8745, 1.814658325))
            Line((-2.8745, 1.814658325), (-4.064391671, 3.005766654))
            Line((-4.064391671, 3.005766654), (-3.004391671, 4.065766654))
            Line((-3.004391671, 4.065766654), (-1.8145, 2.874658325))
            ThreePointArc((-1.8145, 2.874658325), (0, 3.399316649), (1.8145, 2.874658325))
            Line((1.8145, 2.874658325), (3.0055, 4.065658325))
            Line((3.0055, 4.065658325), (4.066608329, 3.004549996))
            Line((4.066608329, 3.004549996), (2.8755, 1.814658325))
            ThreePointArc((2.8755, 1.814658325), (3.400473913, -0.000341675), (2.8755, -1.815341675))
            Line((2.8755, -1.815341675), (4.066608329, -3.005233346))
            Line((4.066608329, -3.005233346), (3.0055, -4.066341675))
            Line((3.0055, -4.066341675), (1.8145, -2.875341675))
            ThreePointArc((1.8145, -2.875341675), (0, -3.4), (-1.8145, -2.875341675))
        make_face(mode=Mode.SUBTRACT)
        with BuildLine():
            Line((-17.9995, -15.500341675), (-17.9995, -11.800341675))
            Line((-17.9995, -11.800341675), (-11.7995, -11.800341675))
            Line((-11.7995, -11.800341675), (-11.7995, -18.000341675))
            Line((-11.7995, -18.000341675), (-15.4995, -18.000341675))
            ThreePointArc((-15.4995, -18.000341675), (-17.267266953, -17.268108628), (-17.9995, -15.500341675))
        make_face(mode=Mode.SUBTRACT)
        with BuildLine():
            Line((-11.7995, 17.999658325), (-11.7995, 11.799658325))
            Line((-11.7995, 11.799658325), (-17.9995, 11.799658325))
            Line((-17.9995, 11.799658325), (-17.9995, 15.499658325))
            ThreePointArc((-17.9995, 15.499658325), (-17.267266953, 17.267425278), (-15.4995, 17.999658325))
            Line((-15.4995, 17.999658325), (-11.7995, 17.999658325))
        make_face(mode=Mode.SUBTRACT)
    extrude(amount=-EXTRUDE_1_DEPTH)


solid = part.part
